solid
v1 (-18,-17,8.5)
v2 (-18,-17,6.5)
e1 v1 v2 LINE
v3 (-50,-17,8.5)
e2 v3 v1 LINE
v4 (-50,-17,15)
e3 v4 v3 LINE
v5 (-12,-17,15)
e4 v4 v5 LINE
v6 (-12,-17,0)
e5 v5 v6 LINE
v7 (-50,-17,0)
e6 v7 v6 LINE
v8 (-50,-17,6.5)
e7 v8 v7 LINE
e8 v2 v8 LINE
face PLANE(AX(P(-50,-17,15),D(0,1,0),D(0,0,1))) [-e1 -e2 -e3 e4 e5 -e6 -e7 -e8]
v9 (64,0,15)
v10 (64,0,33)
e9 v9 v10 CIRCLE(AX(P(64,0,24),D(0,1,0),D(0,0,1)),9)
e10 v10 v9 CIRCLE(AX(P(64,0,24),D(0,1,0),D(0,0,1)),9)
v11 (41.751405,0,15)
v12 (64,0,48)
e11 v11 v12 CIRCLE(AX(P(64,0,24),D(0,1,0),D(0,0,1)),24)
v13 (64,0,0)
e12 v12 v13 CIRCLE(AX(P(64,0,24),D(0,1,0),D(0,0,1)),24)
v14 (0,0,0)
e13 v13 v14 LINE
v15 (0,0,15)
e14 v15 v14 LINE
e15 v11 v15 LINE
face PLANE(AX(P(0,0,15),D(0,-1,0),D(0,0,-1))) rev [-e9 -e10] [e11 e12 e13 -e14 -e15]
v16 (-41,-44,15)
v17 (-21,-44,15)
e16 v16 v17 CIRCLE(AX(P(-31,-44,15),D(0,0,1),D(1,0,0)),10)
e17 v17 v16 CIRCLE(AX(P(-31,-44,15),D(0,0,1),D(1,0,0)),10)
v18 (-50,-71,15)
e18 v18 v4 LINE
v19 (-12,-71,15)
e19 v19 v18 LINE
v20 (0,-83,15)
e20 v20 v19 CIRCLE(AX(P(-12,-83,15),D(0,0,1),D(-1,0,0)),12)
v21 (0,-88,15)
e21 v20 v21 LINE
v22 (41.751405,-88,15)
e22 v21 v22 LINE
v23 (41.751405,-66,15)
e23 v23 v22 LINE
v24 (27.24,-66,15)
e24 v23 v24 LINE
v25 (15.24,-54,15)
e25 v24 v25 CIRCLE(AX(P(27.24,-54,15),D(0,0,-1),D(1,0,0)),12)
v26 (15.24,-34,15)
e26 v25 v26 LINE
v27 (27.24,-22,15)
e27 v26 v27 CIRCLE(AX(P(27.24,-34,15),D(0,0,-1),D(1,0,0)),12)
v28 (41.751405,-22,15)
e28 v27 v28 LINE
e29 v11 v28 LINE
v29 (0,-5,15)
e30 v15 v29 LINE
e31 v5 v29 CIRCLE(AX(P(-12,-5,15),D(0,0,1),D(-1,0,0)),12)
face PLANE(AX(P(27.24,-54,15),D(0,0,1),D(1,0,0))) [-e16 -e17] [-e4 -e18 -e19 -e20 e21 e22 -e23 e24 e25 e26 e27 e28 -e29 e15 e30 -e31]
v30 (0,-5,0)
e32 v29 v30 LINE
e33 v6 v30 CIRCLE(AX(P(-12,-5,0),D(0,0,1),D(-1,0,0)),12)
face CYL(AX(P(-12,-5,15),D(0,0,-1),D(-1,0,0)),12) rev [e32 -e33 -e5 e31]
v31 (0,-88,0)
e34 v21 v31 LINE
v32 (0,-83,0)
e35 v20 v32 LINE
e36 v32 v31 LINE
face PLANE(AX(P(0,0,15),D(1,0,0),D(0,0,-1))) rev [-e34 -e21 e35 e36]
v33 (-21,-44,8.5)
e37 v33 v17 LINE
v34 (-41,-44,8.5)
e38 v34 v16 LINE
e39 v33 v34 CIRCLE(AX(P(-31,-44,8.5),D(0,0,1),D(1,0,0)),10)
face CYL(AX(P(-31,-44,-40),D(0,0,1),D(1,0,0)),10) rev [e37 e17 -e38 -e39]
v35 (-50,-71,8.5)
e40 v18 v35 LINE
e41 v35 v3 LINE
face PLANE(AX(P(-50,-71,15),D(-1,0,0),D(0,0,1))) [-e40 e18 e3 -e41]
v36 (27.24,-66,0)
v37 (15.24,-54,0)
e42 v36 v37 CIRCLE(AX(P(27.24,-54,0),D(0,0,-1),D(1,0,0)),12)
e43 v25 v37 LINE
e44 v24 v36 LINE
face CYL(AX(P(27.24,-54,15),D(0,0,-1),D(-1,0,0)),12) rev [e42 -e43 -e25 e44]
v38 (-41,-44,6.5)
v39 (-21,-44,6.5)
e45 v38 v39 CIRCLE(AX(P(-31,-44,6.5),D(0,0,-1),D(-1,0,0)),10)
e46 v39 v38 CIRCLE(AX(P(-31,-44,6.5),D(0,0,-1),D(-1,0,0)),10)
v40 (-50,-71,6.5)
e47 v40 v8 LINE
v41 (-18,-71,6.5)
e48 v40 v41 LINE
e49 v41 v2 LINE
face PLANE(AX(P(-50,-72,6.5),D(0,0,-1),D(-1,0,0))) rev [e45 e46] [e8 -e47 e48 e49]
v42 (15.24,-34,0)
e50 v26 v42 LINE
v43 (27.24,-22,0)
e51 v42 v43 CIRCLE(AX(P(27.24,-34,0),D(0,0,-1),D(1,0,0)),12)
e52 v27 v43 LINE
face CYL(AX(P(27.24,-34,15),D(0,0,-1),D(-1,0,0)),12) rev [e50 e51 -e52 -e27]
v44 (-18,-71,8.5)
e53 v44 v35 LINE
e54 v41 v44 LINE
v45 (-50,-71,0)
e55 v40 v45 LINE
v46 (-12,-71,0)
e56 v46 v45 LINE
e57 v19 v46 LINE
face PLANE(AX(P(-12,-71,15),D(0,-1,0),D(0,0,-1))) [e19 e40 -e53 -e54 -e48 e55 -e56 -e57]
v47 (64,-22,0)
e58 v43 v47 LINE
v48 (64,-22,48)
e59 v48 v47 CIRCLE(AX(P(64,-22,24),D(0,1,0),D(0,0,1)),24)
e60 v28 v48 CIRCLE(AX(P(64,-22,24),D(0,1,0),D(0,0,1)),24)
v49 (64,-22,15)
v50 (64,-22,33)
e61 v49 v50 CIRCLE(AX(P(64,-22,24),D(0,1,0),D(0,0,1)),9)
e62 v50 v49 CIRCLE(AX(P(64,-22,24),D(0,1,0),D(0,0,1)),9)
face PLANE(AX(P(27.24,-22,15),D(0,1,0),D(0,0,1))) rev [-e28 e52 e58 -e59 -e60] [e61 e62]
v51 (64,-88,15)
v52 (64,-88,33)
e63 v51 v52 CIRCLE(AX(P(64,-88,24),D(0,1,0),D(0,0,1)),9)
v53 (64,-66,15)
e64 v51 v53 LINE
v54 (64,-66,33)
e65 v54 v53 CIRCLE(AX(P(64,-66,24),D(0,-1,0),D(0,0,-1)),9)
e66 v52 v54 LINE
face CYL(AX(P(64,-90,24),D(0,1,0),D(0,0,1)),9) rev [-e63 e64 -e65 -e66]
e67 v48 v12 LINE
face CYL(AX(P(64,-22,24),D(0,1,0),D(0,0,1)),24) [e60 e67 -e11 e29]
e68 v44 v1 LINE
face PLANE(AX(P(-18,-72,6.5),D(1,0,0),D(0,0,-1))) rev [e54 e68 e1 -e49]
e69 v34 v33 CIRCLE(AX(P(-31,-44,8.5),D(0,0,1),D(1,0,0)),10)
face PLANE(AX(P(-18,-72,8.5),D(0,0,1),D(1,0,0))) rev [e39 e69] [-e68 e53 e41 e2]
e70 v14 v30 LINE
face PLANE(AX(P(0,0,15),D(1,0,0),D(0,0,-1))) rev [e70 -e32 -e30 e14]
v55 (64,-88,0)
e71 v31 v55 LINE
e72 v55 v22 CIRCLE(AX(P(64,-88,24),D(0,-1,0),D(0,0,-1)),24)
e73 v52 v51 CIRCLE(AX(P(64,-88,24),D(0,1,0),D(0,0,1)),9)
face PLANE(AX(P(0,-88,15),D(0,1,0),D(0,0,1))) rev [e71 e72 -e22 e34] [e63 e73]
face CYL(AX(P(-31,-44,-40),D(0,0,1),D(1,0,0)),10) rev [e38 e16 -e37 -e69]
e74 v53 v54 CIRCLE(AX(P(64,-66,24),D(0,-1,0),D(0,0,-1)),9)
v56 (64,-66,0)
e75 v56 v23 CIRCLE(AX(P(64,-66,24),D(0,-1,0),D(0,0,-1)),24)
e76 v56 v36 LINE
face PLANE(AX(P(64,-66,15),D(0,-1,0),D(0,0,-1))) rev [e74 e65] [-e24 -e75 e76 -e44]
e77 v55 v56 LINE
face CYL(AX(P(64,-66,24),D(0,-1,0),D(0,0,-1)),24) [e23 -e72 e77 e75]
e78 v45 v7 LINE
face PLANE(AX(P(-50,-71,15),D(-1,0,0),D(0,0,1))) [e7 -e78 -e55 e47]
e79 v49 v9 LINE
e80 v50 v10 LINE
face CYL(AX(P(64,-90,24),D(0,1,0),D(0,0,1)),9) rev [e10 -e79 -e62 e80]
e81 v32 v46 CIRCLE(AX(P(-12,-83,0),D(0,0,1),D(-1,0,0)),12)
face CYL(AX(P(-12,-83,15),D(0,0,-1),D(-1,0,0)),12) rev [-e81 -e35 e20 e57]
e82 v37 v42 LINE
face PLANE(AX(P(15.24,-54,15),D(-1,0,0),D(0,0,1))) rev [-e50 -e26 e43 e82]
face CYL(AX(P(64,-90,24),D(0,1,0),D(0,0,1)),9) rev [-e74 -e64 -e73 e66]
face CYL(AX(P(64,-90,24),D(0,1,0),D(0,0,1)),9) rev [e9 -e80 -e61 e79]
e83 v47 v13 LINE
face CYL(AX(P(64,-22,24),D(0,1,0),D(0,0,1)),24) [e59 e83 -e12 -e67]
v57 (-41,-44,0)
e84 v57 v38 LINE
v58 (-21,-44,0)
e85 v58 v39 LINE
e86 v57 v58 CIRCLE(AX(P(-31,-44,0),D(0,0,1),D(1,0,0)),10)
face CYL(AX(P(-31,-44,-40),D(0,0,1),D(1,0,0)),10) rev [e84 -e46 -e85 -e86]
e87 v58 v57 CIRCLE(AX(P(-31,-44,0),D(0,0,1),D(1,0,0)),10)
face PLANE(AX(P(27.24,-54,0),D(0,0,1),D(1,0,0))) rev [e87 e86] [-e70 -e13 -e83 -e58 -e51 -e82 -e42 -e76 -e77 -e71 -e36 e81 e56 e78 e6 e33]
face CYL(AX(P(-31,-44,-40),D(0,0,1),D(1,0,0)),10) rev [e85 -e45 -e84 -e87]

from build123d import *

# Parameters (mm, degrees)
BASE_PLATE_DEPTH         = 15
PIVOT_BOSS_1_PROFILE_R   = 24
PIVOT_BOSS_1_DEPTH       = 22
PIVOT_START              = -22
PIVOT_BOSS_2_PROFILE_R   = 24
PIVOT_BOSS_2_DEPTH       = 22
UPRIGHT_WEB_DEPTH        = 15
WEB_SLOT_DEPTH           = 55
WEB_HOLE_PROFILE_R       = 10
WEB_HOLE_DEPTH           = 55
PIVOT_BORE_PROFILE_R     = 9
PIVOT_BORE_THROUGH_DEPTH = 90


with BuildPart() as part:
    # Base Plate Profile → Base Plate (new body)
    with BuildSketch(Plane.XY):
        with BuildLine():
            Line((0, 0), (64, 0))
            Line((64, 0), (64, -22))
            Line((64, -22), (27.24, -22))
            ThreePointArc((27.24, -22), (18.754718626, -25.514718626), (15.24, -34))
            Line((15.24, -34), (15.24, -54))
            ThreePointArc((15.24, -54), (18.754718626, -62.485281374), (27.24, -66))
            Line((27.24, -66), (64, -66))
            Line((64, -66), (64, -88))
            Line((64, -88), (0, -88))
            Line((0, -88), (0, 0))
        make_face()
    extrude(amount=BASE_PLATE_DEPTH)

    # Pivot Boss 1 Profile → Pivot Boss 1 (add)
    with BuildSketch(Plane(origin=(0, 0, 0), x_dir=(1, 0, 0), z_dir=(0, 1, 0))):
        with Locations((64, -24)):
            Circle(PIVOT_BOSS_1_PROFILE_R)
    extrude(amount=-PIVOT_BOSS_1_DEPTH)

    # Pivot Boss 2 Profile → Pivot Boss 2 (add)
    with BuildSketch(Plane.XZ.offset(88).offset(PIVOT_START)):
        with Locations((64, 24)):
            Circle(PIVOT_BOSS_2_PROFILE_R)
    extrude(amount=PIVOT_BOSS_2_DEPTH)

    # Upright Web Profile → Upright Web (add)
    with BuildSketch(Plane(origin=(0, 0, 0), x_dir=(-1, 0, 0), z_dir=(0, 0, -1))):
        with BuildLine():
            Line((0, -44), (0, -17))
            Line((0, -17), (0, -5))
            ThreePointArc((0, -5), (3.514718626, -13.485281374), (12, -17))
            Line((12, -17), (50, -17))
            Line((50, -17), (50, -71))
            Line((50, -71), (12, -71))
            ThreePointArc((12, -71), (3.514718626, -74.514718626), (0, -83))
            Line((0, -83), (0, -71))
            Line((0, -71), (0, -44))
        make_face()
    extrude(amount=-UPRIGHT_WEB_DEPTH)

    # Web Slot Profile → Web Slot (cut)
    with BuildSketch(Plane(origin=(0, -17, 0), x_dir=(1, 0, 0), z_dir=(0, 1, 0))):
        Polygon((-50, -7.5), (-50, -6.5), (-18, -6.5), (-18, -8.5), (-50, -8.5), align=None)
    extrude(amount=-WEB_SLOT_DEPTH, mode=Mode.SUBTRACT)

    # Web Hole Profile → Web Hole (cut)
    with BuildSketch(Plane.XY.offset(15)):
        with Locations((-31, -44)):
            Circle(WEB_HOLE_PROFILE_R)
    extrude(amount=-WEB_HOLE_DEPTH, mode=Mode.SUBTRACT)

    # Pivot Bore Profile → Pivot Bore Through (cut)
    with BuildSketch(Plane(origin=(0, 0, 0), x_dir=(1, 0, 0), z_dir=(0, 1, 0))):
        with Locations(Location((64, -24, 0), (0, 0, 270))):
            Circle(PIVOT_BORE_PROFILE_R)
    extrude(amount=-PIVOT_BORE_THROUGH_DEPTH, mode=Mode.SUBTRACT)


solid = part.part
